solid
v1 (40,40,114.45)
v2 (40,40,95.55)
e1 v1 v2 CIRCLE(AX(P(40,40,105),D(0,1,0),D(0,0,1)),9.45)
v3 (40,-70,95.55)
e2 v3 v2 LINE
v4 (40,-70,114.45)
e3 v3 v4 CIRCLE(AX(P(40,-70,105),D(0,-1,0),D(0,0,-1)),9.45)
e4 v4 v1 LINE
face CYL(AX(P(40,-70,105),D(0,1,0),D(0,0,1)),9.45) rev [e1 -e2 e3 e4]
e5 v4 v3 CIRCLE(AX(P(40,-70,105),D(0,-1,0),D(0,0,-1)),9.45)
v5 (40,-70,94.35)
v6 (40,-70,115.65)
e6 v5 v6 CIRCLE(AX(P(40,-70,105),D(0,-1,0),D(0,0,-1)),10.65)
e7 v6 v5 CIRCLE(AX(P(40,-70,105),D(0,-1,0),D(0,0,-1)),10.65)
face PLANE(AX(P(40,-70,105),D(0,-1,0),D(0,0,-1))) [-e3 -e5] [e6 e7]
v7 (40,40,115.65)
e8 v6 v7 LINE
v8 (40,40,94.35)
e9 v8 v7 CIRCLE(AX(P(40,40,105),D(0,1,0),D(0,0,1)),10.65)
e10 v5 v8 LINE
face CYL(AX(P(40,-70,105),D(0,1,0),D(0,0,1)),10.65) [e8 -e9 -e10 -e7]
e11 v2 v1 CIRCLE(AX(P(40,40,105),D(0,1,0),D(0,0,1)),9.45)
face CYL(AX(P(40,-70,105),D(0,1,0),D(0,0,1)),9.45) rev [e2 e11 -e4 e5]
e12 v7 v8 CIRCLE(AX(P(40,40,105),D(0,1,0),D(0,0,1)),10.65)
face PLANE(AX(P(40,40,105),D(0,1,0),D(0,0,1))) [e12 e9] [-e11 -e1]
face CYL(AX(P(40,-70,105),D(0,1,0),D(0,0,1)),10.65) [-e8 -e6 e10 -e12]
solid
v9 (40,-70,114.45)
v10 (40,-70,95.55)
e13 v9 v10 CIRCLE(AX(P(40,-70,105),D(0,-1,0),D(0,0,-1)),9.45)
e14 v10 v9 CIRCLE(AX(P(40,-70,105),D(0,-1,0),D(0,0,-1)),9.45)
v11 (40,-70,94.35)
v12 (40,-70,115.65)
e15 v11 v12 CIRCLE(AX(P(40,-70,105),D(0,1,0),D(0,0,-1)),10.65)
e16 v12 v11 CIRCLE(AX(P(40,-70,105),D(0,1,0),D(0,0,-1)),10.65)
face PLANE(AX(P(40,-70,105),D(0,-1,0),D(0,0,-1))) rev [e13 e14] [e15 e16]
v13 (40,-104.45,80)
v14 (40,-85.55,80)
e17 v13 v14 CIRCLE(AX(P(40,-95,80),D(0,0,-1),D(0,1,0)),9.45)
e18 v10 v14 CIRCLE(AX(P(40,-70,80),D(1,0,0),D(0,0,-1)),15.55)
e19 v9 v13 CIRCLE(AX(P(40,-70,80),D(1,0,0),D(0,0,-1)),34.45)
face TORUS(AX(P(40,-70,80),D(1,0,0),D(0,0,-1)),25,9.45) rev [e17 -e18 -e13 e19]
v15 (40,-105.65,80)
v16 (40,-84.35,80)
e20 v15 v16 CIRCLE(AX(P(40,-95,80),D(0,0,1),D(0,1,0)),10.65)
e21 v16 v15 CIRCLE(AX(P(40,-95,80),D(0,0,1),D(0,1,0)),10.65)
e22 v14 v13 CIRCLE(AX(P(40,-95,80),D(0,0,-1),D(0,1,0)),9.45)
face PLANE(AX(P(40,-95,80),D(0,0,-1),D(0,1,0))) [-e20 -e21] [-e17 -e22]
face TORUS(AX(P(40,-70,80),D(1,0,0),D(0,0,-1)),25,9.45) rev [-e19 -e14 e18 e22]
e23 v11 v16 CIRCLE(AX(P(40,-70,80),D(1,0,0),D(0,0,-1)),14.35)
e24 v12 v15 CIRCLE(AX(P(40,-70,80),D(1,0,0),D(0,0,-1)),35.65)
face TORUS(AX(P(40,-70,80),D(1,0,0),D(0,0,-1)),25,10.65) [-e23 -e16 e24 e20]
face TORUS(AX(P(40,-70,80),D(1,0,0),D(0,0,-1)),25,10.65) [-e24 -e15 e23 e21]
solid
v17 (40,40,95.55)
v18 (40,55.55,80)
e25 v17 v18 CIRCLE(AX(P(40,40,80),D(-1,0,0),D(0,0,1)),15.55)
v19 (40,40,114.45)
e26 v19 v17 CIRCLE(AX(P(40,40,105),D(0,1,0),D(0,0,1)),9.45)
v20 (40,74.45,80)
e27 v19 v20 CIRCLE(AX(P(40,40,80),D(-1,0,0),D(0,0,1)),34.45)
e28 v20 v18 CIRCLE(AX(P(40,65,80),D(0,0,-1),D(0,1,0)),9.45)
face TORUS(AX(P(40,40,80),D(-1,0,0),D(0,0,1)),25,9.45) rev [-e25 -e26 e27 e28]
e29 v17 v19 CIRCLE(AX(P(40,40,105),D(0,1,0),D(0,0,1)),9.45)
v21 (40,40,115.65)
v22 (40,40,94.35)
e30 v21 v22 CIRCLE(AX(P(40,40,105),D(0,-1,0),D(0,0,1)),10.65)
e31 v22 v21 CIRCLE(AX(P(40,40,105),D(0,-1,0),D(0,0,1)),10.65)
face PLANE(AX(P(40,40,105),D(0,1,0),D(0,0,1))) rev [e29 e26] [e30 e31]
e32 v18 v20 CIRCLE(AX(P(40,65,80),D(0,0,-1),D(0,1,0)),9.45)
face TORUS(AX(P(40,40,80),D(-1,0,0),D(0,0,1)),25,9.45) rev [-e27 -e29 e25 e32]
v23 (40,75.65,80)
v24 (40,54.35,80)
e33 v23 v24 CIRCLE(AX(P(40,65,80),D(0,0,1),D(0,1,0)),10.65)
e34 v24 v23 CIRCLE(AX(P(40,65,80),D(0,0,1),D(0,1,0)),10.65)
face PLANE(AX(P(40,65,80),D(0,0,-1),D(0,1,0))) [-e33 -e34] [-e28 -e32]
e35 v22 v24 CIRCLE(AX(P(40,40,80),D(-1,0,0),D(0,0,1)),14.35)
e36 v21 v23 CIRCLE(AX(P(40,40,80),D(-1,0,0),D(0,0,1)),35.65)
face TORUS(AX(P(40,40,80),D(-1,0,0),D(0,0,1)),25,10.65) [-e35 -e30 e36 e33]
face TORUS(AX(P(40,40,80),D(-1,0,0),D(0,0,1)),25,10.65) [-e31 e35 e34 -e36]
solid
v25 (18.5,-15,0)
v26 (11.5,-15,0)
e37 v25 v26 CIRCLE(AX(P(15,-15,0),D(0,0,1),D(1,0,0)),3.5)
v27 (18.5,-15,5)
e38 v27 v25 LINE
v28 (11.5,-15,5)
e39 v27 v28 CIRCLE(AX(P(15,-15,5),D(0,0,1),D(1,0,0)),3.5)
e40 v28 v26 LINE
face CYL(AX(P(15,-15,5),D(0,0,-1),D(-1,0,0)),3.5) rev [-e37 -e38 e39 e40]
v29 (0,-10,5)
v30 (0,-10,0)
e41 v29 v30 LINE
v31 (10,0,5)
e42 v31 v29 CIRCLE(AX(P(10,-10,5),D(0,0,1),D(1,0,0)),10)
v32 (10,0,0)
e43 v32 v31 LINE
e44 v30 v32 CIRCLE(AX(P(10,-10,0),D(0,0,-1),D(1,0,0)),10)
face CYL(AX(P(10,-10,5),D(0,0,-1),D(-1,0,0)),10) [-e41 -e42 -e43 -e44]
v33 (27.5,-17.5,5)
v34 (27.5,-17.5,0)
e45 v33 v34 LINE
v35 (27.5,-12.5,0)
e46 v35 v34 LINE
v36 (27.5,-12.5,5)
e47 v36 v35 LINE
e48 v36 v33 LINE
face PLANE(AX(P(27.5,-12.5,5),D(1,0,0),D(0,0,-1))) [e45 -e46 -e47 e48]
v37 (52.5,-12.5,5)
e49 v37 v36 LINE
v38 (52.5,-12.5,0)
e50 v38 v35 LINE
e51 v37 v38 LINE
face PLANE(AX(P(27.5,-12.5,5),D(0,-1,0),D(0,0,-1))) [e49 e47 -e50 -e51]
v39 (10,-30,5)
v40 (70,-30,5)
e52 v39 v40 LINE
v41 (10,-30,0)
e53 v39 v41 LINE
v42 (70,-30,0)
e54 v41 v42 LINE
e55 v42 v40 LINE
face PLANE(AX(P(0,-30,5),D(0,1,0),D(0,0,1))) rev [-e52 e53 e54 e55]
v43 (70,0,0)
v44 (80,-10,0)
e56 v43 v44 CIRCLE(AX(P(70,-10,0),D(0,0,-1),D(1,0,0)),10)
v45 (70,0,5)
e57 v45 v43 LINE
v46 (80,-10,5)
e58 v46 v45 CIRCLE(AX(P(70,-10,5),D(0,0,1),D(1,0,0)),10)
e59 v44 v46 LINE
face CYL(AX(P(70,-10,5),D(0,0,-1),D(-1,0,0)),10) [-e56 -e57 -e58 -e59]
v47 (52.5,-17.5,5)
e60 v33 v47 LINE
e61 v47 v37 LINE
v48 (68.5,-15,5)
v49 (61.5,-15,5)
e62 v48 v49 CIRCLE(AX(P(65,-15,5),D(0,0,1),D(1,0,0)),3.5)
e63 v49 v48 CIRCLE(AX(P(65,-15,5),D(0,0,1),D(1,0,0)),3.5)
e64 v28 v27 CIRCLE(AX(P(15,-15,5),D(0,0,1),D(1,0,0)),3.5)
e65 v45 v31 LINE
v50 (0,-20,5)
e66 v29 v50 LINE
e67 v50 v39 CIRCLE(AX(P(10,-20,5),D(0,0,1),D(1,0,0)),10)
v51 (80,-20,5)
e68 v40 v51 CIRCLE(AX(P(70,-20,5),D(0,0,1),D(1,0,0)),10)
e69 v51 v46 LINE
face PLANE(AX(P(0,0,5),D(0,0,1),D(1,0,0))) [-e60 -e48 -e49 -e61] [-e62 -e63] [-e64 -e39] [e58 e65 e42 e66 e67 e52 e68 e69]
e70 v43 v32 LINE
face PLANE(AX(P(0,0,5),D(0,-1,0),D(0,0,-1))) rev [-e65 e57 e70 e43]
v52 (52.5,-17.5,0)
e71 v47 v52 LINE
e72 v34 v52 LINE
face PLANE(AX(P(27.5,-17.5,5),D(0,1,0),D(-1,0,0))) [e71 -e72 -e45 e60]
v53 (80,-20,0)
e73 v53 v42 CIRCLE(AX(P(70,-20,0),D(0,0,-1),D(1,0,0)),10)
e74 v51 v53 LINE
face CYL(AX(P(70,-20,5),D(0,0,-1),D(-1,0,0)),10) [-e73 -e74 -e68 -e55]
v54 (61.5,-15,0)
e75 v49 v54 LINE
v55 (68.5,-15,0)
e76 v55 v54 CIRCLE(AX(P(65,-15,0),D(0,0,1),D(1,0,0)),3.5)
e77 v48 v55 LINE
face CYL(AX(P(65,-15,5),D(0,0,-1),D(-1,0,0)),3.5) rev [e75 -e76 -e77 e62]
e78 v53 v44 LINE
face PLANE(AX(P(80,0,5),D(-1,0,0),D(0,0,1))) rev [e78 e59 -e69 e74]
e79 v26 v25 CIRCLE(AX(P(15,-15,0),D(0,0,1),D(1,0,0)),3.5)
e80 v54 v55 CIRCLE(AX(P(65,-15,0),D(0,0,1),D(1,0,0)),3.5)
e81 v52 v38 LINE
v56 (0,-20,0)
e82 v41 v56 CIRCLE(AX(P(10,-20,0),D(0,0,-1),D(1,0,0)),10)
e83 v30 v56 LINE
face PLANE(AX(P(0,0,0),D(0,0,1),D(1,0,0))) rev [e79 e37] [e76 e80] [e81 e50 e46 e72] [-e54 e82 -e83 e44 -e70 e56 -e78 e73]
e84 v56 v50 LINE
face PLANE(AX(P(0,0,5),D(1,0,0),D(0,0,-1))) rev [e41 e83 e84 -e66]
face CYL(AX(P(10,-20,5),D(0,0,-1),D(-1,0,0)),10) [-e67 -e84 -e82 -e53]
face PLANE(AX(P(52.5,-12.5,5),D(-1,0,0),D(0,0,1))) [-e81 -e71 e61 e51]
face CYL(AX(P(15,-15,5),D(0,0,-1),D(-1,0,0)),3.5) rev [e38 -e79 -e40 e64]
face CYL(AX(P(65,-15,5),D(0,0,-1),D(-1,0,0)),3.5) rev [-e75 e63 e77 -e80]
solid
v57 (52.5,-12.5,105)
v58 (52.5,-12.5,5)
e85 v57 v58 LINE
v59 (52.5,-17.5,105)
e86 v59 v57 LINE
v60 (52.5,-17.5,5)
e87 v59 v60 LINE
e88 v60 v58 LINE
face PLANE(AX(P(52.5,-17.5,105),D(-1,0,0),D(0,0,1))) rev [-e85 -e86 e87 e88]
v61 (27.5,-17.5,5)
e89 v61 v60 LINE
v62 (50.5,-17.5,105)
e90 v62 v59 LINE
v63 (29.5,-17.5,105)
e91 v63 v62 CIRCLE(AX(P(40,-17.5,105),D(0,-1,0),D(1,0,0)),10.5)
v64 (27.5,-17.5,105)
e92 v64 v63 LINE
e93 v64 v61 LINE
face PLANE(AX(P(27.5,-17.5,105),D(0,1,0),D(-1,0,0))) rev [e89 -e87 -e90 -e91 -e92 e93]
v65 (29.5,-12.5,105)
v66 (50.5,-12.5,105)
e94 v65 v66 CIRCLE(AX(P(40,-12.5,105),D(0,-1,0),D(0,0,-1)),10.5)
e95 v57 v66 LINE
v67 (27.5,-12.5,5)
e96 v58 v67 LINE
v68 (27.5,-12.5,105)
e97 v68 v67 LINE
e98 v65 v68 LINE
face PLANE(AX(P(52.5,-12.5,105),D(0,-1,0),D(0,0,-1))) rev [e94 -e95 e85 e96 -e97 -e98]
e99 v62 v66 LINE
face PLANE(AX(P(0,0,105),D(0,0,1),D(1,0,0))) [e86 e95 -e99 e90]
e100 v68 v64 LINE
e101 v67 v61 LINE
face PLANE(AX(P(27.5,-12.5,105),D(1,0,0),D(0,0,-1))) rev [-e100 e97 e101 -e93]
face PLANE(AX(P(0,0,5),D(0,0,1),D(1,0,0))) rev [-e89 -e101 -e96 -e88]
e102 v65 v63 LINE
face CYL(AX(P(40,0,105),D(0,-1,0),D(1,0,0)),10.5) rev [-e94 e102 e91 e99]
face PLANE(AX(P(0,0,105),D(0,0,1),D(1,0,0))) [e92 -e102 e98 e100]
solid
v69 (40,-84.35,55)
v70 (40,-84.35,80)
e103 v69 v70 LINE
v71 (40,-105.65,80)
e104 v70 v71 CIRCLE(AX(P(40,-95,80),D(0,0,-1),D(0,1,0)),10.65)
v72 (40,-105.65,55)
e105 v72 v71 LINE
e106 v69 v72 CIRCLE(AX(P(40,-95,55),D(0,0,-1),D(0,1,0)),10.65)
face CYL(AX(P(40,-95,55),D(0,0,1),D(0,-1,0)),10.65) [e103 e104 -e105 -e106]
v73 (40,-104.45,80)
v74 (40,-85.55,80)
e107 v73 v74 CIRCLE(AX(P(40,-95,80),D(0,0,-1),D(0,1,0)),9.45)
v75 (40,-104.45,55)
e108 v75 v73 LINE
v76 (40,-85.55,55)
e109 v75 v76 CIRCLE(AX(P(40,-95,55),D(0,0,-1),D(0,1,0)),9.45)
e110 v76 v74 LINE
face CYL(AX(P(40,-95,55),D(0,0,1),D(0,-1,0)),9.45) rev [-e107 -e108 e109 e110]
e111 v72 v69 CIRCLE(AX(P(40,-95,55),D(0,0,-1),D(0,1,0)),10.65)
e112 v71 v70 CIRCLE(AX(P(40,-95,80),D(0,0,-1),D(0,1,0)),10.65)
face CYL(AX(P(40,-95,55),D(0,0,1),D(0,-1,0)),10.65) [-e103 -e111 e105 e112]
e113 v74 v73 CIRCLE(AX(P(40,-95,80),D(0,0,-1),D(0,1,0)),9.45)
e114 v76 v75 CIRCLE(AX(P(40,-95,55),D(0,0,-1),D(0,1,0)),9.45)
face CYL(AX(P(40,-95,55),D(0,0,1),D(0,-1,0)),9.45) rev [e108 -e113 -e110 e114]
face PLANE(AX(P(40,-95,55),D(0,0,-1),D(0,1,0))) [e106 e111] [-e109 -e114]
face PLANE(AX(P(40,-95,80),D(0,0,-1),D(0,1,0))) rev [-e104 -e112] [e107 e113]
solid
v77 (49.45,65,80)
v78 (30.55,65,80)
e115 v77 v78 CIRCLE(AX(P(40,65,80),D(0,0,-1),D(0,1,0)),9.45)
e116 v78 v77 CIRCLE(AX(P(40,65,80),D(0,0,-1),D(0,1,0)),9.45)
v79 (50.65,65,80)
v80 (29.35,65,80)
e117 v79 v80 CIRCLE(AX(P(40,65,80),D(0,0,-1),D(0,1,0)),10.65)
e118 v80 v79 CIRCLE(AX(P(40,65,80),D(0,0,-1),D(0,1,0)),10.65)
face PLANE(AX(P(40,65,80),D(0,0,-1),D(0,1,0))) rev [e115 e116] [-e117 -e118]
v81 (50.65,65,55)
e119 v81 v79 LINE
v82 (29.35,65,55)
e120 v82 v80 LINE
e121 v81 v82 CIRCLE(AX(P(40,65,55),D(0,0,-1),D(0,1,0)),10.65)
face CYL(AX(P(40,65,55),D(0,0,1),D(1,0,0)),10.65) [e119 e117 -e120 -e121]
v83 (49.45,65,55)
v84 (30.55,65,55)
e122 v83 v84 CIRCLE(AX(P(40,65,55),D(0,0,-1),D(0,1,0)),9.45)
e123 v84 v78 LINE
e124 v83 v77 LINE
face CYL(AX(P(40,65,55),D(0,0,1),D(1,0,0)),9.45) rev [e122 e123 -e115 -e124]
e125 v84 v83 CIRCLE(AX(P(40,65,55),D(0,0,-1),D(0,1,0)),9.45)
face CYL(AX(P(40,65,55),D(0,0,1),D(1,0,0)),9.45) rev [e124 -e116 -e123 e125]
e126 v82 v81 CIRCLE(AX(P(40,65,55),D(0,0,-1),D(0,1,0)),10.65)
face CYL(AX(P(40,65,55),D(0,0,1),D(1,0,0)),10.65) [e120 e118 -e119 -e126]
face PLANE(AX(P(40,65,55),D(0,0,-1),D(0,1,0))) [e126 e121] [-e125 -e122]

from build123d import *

# Parameters (mm, degrees)
SKETCH_1_W                                    = 80
SKETCH_1_H                                    = 30
SKETCH_1_R                                    = 3.5
SKETCH_1_W_2                                  = 25
SKETCH_1_H_2                                  = 5
BOSS_EXTRUDE1_DEPTH                           = 5
FILLET1_R                                     = 10
SKETCH4_W                                     = 25
SKETCH4_H                                     = 5
BOSS_EXTRUDE2_DEPTH                           = 100
SKETCH5_R                                     = 10.5
CUT_EXTRUDE1_DEPTH                            = 134.158739856
SKETCH1_R                                     = 10.65
SKETCH1_R_2                                   = 9.45
GB_T_6728_2002_ROUND_TUBE_021_3_X_1_2_2_DEPTH = 110
SKETCH1_ON_SEGMENT_2_R                        = 10.65
SKETCH1_ON_SEGMENT_2_R_2                      = 9.45
GB_T_6728_2002_ROUND_TUBE_021_3_X_1_2_ANGLE   = 90
SKETCH1_ON_SEGMENT_3_R                        = 10.65
SKETCH1_ON_SEGMENT_3_R_2                      = 9.45
GB_T_6728_2002_ROUND_TUBE_021_3_X_1_3_ANGLE   = 90
SKETCH1_ON_SEGMENT_4_R                        = 10.65
SKETCH1_ON_SEGMENT_4_R_2                      = 9.45
GB_T_6728_2002_ROUND_TUBE_021_3_X_1_4_DEPTH   = 25
SKETCH1_ON_SEGMENT_5_R                        = 10.65
SKETCH1_ON_SEGMENT_5_R_2                      = 9.45
GB_T_6728_2002_ROUND_TUBE_021_3_X_1_5_DEPTH   = 25


with BuildPart() as part:
    # Sketch 1 → Boss-Extrude1 (new body)
    with BuildSketch(Plane.XY):
        with Locations((40, -15)):
            Rectangle(SKETCH_1_W, SKETCH_1_H)
        with Locations((15, -15)):
            Circle(SKETCH_1_R, mode=Mode.SUBTRACT)
        with Locations((65, -15)):
            Circle(SKETCH_1_R, mode=Mode.SUBTRACT)
        with Locations((40, -15)):
            Rectangle(SKETCH_1_W_2, SKETCH_1_H_2, mode=Mode.SUBTRACT)
    extrude(amount=BOSS_EXTRUDE1_DEPTH)

    # Fillet1
    fillet1_edges = [part.edges().sort_by_distance(p)[0] for p in [
        (0, 0, 2.5),
        (80, 0, 2.5),
        (80, -30, 2.5),
        (0, -30, 2.5),
    ]]
    fillet(fillet1_edges, radius=FILLET1_R)


with BuildPart() as body_2:
    # Sketch4 → Boss-Extrude2 (new body)
    with BuildSketch(Plane.XY.offset(5)):
        with Locations((40, -15)):
            Rectangle(SKETCH4_W, SKETCH4_H)
    extrude(amount=BOSS_EXTRUDE2_DEPTH)

    # Sketch5 → Cut-Extrude1 (cut, through all)
    with BuildSketch(Plane.XZ.offset(17.5)):
        with Locations((40, 105)):
            Circle(SKETCH5_R)
    extrude(amount=-CUT_EXTRUDE1_DEPTH, mode=Mode.SUBTRACT)


with BuildPart() as body_3:
    # Sketch1 → GB/T 6728-2002 round tube 021.3 X 1.2(2) (new body)
    with BuildSketch(Plane(origin=(40, 40, 105), x_dir=(1, 0, 0), z_dir=(0, -1, 0))):
        Circle(SKETCH1_R)
        Circle(SKETCH1_R_2, mode=Mode.SUBTRACT)
    extrude(amount=GB_T_6728_2002_ROUND_TUBE_021_3_X_1_2_2_DEPTH)


with BuildPart() as body_4:
    # Sketch1 on segment 2 (carried to the start of arc 2) → GB_T 6728-2002 round tube 021.3 X 1. 2 (revolve)
    with BuildSketch(Plane(origin=(40, 40, 105), x_dir=(1, 0, 0), z_dir=(0, 1, 0))):
        Circle(SKETCH1_ON_SEGMENT_2_R)
        Circle(SKETCH1_ON_SEGMENT_2_R_2, mode=Mode.SUBTRACT)
    revolve(axis=Axis((40, 40, 80), (-1, 0, 0)), revolution_arc=GB_T_6728_2002_ROUND_TUBE_021_3_X_1_2_ANGLE)


with BuildPart() as body_5:
    # Sketch1 on segment 3 (carried to the start of arc 3) → GB_T 6728-2002 round tube 021.3 X 1. 3 (revolve)
    with BuildSketch(Plane(origin=(40, -70, 105), x_dir=(1, 0, 0), z_dir=(0, -1, 0))):
        Circle(SKETCH1_ON_SEGMENT_3_R)
        Circle(SKETCH1_ON_SEGMENT_3_R_2, mode=Mode.SUBTRACT)
    revolve(axis=Axis((40, -70, 80), (1, 0, 0)), revolution_arc=GB_T_6728_2002_ROUND_TUBE_021_3_X_1_3_ANGLE)


with BuildPart() as body_6:
    # Sketch1 on segment 4 (carried to segment 4) → GB_T 6728-2002 round tube 021.3 X 1. 4 (new body)
    with BuildSketch(Plane(origin=(40, -95, 80), x_dir=(1, 0, 0), z_dir=(0, 0, -1))):
        Circle(SKETCH1_ON_SEGMENT_4_R)
        Circle(SKETCH1_ON_SEGMENT_4_R_2, mode=Mode.SUBTRACT)
    extrude(amount=GB_T_6728_2002_ROUND_TUBE_021_3_X_1_4_DEPTH)


with BuildPart() as body_7:
    # Sketch1 on segment 5 (carried to segment 5) → GB_T 6728-2002 round tube 021.3 X 1. 5 (new body)
    with BuildSketch(Plane(origin=(40, 65, 80), x_dir=(1, 0, 0), z_dir=(0, 0, -1))):
        Circle(SKETCH1_ON_SEGMENT_5_R)
        Circle(SKETCH1_ON_SEGMENT_5_R_2, mode=Mode.SUBTRACT)
    extrude(amount=GB_T_6728_2002_ROUND_TUBE_021_3_X_1_5_DEPTH)


solid = Compound([part.part, body_2.part, body_3.part, body_4.part, body_5.part, body_6.part, body_7.part])
